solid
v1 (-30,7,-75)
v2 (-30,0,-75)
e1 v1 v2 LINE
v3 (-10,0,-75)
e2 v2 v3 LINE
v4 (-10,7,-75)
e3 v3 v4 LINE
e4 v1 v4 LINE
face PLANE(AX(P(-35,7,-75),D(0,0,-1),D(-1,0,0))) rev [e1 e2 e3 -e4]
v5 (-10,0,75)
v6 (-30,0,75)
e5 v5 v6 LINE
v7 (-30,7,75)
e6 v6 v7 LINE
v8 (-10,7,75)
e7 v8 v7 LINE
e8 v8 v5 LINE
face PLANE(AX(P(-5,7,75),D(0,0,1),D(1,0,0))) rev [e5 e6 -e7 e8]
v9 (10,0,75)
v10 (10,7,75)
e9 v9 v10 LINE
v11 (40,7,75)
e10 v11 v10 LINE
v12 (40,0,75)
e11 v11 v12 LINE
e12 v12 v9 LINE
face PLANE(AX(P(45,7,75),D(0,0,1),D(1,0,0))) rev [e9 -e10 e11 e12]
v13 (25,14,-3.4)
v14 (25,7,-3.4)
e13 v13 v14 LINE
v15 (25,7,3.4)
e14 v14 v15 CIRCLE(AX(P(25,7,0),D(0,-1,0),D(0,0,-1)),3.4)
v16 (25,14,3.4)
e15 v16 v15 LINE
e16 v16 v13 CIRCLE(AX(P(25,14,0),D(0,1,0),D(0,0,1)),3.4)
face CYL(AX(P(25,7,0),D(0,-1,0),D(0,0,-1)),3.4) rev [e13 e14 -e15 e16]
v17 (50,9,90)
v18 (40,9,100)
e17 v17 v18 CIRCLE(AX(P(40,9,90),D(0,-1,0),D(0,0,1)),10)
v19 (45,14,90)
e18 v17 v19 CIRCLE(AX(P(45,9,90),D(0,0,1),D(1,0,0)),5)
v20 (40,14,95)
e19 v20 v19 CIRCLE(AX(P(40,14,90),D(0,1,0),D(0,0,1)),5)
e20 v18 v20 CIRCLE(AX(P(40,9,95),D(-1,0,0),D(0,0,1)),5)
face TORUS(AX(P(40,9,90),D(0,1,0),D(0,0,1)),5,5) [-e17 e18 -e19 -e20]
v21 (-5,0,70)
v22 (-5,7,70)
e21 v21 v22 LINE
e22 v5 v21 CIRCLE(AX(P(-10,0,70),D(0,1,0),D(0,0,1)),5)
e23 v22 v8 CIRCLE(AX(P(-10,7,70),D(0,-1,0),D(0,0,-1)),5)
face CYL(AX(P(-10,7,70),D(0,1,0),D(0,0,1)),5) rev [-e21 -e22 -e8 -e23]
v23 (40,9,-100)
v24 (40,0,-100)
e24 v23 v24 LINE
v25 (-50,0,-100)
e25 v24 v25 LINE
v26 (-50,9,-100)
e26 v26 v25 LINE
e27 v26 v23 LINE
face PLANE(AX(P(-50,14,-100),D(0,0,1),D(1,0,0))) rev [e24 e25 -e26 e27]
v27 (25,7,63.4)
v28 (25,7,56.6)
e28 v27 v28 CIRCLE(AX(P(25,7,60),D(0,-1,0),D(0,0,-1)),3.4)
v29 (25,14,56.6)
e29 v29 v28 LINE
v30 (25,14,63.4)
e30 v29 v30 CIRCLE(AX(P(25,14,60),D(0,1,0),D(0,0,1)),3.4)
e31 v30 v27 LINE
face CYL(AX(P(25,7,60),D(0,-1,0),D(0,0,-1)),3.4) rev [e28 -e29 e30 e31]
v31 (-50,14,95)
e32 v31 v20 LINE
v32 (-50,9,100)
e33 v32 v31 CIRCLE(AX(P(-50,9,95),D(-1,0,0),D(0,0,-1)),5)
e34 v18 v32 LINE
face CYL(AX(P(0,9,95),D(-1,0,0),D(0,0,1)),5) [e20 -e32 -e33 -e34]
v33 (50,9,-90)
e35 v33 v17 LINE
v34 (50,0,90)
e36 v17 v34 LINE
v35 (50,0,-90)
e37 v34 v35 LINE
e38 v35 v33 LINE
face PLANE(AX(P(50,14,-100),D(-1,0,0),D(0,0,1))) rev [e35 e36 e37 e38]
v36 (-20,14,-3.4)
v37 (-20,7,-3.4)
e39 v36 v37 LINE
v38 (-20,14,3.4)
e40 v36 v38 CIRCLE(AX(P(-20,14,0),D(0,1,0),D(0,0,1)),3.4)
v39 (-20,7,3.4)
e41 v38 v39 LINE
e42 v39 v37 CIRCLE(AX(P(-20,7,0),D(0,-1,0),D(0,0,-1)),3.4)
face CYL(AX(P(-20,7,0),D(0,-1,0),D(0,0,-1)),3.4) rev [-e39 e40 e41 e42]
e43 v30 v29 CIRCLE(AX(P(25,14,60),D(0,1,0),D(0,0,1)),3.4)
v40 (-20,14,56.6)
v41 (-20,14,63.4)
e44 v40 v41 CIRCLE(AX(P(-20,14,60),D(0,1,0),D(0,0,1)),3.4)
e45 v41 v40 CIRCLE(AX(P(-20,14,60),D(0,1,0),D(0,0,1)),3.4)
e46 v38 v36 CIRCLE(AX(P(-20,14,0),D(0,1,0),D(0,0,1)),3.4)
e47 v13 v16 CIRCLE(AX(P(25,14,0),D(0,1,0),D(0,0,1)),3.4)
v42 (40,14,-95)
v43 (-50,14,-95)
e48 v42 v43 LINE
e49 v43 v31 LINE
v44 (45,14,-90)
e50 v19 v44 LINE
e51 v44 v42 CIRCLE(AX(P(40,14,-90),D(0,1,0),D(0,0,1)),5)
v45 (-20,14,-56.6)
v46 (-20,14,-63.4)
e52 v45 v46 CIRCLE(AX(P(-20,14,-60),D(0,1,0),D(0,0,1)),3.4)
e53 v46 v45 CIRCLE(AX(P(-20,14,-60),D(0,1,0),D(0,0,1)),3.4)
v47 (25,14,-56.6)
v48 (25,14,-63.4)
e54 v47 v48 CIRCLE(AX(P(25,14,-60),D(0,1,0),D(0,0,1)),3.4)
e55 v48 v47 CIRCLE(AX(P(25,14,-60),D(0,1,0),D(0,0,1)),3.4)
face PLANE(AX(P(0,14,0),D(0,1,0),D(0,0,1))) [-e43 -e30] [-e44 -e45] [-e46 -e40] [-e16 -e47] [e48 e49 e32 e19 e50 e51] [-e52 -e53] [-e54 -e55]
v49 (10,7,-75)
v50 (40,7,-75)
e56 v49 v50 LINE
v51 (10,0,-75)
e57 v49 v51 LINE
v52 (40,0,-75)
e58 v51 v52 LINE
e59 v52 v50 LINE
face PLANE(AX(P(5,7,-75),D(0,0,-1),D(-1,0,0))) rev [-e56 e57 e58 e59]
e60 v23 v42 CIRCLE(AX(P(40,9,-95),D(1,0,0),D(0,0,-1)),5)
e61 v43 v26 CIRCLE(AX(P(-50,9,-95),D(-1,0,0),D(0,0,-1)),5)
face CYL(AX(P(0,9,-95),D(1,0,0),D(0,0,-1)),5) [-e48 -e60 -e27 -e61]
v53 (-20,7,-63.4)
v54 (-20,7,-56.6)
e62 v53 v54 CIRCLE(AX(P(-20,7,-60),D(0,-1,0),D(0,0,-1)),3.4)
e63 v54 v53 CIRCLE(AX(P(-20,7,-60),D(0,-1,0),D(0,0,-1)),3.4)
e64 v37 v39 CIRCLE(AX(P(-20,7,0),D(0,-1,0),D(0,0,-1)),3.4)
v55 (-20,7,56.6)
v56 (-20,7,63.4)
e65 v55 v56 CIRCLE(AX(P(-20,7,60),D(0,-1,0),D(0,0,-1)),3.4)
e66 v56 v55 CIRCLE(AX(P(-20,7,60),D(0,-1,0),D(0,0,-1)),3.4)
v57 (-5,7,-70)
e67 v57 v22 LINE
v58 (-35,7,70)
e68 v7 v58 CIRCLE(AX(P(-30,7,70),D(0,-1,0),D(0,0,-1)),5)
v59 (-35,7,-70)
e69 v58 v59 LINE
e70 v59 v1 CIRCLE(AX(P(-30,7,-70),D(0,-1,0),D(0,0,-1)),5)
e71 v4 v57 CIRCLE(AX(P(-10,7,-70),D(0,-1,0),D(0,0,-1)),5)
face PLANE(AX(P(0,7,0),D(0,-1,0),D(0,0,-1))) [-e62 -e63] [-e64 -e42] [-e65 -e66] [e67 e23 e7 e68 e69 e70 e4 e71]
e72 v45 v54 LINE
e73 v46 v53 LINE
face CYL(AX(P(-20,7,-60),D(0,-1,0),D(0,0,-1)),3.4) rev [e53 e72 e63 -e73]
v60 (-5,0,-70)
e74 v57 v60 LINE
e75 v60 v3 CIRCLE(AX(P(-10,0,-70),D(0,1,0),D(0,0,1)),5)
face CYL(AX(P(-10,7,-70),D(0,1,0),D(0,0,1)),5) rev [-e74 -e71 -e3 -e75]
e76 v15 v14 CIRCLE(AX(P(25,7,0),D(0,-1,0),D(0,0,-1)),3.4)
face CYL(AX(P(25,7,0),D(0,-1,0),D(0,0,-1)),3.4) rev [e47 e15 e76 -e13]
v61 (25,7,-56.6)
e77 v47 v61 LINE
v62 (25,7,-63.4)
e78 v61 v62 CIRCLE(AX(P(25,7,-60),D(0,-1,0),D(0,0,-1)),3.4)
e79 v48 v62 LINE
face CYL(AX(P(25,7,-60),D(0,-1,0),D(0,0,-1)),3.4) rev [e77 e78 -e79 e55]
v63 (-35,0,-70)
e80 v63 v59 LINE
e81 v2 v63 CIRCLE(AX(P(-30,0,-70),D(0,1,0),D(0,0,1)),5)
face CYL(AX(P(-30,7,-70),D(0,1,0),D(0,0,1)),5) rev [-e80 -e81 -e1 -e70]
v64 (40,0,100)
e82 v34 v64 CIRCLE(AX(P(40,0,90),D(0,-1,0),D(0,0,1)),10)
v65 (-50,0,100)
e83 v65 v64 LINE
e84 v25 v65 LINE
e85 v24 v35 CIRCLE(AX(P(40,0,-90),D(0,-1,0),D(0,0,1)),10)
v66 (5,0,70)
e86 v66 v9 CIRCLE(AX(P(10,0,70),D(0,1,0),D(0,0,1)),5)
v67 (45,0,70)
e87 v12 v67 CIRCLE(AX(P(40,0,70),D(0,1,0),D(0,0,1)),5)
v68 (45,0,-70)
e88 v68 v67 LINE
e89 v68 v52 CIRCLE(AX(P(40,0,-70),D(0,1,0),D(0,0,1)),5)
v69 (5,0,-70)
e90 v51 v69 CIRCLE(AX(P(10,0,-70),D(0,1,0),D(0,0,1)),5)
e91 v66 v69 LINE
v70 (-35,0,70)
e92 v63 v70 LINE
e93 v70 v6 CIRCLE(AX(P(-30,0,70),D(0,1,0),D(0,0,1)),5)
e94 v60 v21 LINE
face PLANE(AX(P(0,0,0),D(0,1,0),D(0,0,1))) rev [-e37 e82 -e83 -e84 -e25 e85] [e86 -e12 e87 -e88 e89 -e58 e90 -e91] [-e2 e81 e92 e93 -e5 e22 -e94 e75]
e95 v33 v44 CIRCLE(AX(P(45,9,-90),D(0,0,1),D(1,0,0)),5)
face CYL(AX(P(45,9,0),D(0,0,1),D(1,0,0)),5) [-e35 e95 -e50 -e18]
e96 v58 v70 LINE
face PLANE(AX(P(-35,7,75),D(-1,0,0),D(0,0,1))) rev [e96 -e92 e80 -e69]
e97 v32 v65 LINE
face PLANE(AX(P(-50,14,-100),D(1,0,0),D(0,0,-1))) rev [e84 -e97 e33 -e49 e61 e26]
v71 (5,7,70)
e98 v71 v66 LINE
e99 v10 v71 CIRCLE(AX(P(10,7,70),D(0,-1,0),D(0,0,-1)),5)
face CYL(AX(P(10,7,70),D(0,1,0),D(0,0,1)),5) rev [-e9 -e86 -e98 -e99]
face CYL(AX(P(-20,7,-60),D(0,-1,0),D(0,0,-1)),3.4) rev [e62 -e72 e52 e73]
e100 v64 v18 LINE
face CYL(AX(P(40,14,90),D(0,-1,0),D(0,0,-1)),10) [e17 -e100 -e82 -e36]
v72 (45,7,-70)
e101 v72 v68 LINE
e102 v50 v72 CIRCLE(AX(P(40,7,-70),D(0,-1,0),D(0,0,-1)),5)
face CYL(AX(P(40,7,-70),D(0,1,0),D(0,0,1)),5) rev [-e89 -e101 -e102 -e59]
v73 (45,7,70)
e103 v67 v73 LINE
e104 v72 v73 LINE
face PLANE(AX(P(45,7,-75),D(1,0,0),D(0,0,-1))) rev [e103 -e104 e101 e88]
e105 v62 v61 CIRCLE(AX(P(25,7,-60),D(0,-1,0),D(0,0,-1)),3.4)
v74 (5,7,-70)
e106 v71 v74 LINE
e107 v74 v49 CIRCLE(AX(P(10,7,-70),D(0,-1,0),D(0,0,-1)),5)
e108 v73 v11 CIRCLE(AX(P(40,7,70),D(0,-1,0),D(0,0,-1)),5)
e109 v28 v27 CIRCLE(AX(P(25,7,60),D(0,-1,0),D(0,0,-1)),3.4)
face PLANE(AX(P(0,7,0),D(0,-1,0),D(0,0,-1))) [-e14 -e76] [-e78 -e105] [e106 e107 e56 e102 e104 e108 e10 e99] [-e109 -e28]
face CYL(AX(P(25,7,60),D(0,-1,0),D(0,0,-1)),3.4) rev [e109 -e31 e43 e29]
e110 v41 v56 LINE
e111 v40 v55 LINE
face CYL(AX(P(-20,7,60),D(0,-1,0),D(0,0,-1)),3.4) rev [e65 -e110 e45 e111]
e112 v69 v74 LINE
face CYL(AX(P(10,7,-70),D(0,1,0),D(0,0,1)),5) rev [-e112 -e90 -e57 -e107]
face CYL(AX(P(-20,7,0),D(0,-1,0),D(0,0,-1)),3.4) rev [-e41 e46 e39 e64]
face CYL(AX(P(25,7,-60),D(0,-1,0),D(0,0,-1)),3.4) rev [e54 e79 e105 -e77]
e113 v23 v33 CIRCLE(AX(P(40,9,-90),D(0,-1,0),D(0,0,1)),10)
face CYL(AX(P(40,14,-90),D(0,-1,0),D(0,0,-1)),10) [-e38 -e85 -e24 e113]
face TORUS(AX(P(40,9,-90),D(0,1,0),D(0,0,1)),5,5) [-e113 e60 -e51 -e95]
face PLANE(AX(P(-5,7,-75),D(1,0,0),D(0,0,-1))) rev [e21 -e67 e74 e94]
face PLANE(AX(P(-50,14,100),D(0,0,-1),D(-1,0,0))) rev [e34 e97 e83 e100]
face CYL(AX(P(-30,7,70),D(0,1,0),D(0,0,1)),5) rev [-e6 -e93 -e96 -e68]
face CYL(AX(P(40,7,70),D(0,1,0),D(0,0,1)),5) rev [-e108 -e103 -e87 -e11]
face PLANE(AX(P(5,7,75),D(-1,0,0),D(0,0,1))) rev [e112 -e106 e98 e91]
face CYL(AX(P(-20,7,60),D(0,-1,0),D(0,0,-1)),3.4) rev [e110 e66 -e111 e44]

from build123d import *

# Parameters (mm, degrees)
SKETCH1_W                  = 100
SKETCH1_H                  = 200
BOSS_EXTRUDE1_DEPTH        = 14
FILLET1_R                  = 10
FILLET2_R                  = 5
SKETCH10_W                 = 40
SKETCH10_H                 = 150
BOSS_EXTRUDE3_DEPTH        = 3
SKETCH11_W                 = 10
SKETCH11_H                 = 150
CUT_EXTRUDE5_DEPTH         = 3
SKETCH12_W                 = 40
SKETCH12_H                 = 150
SKETCH12_W_2               = 30
CUT_EXTRUDE6_DEPTH         = 10
M8_TAPPED_HOLE2_AT_2_COUNT = 2
M8_TAPPED_HOLE2_AT_2_PITCH = 60
M8_TAPPED_HOLE2_AT_3_COUNT = 2
M8_TAPPED_HOLE2_AT_3_PITCH = 120
LPATTERN1_COUNT            = 2
LPATTERN1_PITCH            = 45
FILLET3_R                  = 5


with BuildPart() as part:
    # Sketch1 → Boss-Extrude1 (new body)
    with BuildSketch(Plane(origin=(0, 0, 0), x_dir=(1, 0, 0), z_dir=(0, 1, 0))):
        Rectangle(SKETCH1_W, SKETCH1_H)
    extrude(amount=BOSS_EXTRUDE1_DEPTH)

    # Fillet1
    fillet1_edges = [part.edges().sort_by_distance(p)[0] for p in [
        (50, 7, 100),
        (50, 7, -100),
    ]]
    fillet(fillet1_edges, radius=FILLET1_R)

    # Fillet2
    fillet2_edges = [part.edges().sort_by_distance(p)[0] for p in [
        (-5, 14, -100),
        (50, 14, 0),
        (-5, 14, 100),
        (47.071067812, 14, 97.071067812),
        (47.071067812, 14, -97.071067812),
    ]]
    fillet(fillet2_edges, radius=FILLET2_R)

    # Sketch10 → Boss-Extrude3 (add)
    with BuildSketch(Plane.XZ):
        with Locations((-25, 0)):
            Rectangle(SKETCH10_W, SKETCH10_H)
        with Locations((25, 0)):
            Rectangle(SKETCH10_W, SKETCH10_H)
    extrude(amount=BOSS_EXTRUDE3_DEPTH)

    # Sketch11 → Cut-Extrude5 (cut)
    with BuildSketch(Plane.XZ.offset(3)):
        with Locations((-40, 0)):
            Rectangle(SKETCH11_W, SKETCH11_H)
    extrude(amount=-CUT_EXTRUDE5_DEPTH, mode=Mode.SUBTRACT)

    # Sketch12 → Cut-Extrude6 (cut)
    with BuildSketch(Plane.XZ.offset(3)):
        with Locations((25, 0)):
            Rectangle(SKETCH12_W, SKETCH12_H)
        with Locations((-20, 0)):
            Rectangle(SKETCH12_W_2, SKETCH12_H)
    extrude(amount=-CUT_EXTRUDE6_DEPTH, mode=Mode.SUBTRACT)

    # Sketch14 → M8 Tapped Hole2 (revolve, cut)
    with BuildSketch(Plane(origin=(25, 7, -60), x_dir=(0, 0, -1), z_dir=(1, 0, 0))):
        Polygon((0, 0), (0, 21.792926105), (3.4, 19.75), (3.4, 0), align=None)
    m8_tapped_hole2 = revolve(axis=Axis((25, 0.65, -60), (0, 1, 0)), mode=Mode.SUBTRACT)

    # M8 Tapped Hole2 at 2: M8 Tapped Hole2 ×2
    with Locations(*[(0, 0, i * M8_TAPPED_HOLE2_AT_2_PITCH) for i in range(1, M8_TAPPED_HOLE2_AT_2_COUNT)]):
        add(m8_tapped_hole2, mode=Mode.SUBTRACT)

    # M8 Tapped Hole2 at 3: M8 Tapped Hole2 ×2
    with Locations(*[(0, 0, i * M8_TAPPED_HOLE2_AT_3_PITCH) for i in range(1, M8_TAPPED_HOLE2_AT_3_COUNT)]):
        add(m8_tapped_hole2, mode=Mode.SUBTRACT)

    # LPattern1: M8 Tapped Hole2 ×2
    with Locations(*[(-i * LPATTERN1_PITCH, 0, 0) for i in range(1, LPATTERN1_COUNT)]):
        add(m8_tapped_hole2, mode=Mode.SUBTRACT)

    # LPattern1 copy 1 sketch → LPattern1 copy 1 (revolve, cut)
    with BuildSketch(Plane(origin=(-20, 7, 0), x_dir=(0, 0, -1), z_dir=(1, 0, 0))):
        Polygon((0, 0), (0, 21.792926105), (3.4, 19.75), (3.4, 0), align=None)
    revolve(axis=Axis((-20, 0.65, 0), (0, 1, 0)), mode=Mode.SUBTRACT)

    # LPattern1 copy 2 sketch → LPattern1 copy 2 (revolve, cut)
    with BuildSketch(Plane(origin=(-20, 7, 60), x_dir=(0, 0, -1), z_dir=(1, 0, 0))):
        Polygon((0, 0), (0, 21.792926105), (3.4, 19.75), (3.4, 0), align=None)
    revolve(axis=Axis((-20, 0.65, 60), (0, 1, 0)), mode=Mode.SUBTRACT)

    # Fillet3
    fillet3_edges = [part.edges().sort_by_distance(p)[0] for p in [
        (45, 3.5, 75),
        (45, 3.5, -75),
        (5, 3.5, -75),
        (5, 3.5, 75),
        (-5, 3.5, 75),
        (-35, 3.5, -75),
        (-35, 3.5, 75),
        (-5, 3.5, -75),
    ]]
    fillet(fillet3_edges, radius=FILLET3_R)


solid = part.part
